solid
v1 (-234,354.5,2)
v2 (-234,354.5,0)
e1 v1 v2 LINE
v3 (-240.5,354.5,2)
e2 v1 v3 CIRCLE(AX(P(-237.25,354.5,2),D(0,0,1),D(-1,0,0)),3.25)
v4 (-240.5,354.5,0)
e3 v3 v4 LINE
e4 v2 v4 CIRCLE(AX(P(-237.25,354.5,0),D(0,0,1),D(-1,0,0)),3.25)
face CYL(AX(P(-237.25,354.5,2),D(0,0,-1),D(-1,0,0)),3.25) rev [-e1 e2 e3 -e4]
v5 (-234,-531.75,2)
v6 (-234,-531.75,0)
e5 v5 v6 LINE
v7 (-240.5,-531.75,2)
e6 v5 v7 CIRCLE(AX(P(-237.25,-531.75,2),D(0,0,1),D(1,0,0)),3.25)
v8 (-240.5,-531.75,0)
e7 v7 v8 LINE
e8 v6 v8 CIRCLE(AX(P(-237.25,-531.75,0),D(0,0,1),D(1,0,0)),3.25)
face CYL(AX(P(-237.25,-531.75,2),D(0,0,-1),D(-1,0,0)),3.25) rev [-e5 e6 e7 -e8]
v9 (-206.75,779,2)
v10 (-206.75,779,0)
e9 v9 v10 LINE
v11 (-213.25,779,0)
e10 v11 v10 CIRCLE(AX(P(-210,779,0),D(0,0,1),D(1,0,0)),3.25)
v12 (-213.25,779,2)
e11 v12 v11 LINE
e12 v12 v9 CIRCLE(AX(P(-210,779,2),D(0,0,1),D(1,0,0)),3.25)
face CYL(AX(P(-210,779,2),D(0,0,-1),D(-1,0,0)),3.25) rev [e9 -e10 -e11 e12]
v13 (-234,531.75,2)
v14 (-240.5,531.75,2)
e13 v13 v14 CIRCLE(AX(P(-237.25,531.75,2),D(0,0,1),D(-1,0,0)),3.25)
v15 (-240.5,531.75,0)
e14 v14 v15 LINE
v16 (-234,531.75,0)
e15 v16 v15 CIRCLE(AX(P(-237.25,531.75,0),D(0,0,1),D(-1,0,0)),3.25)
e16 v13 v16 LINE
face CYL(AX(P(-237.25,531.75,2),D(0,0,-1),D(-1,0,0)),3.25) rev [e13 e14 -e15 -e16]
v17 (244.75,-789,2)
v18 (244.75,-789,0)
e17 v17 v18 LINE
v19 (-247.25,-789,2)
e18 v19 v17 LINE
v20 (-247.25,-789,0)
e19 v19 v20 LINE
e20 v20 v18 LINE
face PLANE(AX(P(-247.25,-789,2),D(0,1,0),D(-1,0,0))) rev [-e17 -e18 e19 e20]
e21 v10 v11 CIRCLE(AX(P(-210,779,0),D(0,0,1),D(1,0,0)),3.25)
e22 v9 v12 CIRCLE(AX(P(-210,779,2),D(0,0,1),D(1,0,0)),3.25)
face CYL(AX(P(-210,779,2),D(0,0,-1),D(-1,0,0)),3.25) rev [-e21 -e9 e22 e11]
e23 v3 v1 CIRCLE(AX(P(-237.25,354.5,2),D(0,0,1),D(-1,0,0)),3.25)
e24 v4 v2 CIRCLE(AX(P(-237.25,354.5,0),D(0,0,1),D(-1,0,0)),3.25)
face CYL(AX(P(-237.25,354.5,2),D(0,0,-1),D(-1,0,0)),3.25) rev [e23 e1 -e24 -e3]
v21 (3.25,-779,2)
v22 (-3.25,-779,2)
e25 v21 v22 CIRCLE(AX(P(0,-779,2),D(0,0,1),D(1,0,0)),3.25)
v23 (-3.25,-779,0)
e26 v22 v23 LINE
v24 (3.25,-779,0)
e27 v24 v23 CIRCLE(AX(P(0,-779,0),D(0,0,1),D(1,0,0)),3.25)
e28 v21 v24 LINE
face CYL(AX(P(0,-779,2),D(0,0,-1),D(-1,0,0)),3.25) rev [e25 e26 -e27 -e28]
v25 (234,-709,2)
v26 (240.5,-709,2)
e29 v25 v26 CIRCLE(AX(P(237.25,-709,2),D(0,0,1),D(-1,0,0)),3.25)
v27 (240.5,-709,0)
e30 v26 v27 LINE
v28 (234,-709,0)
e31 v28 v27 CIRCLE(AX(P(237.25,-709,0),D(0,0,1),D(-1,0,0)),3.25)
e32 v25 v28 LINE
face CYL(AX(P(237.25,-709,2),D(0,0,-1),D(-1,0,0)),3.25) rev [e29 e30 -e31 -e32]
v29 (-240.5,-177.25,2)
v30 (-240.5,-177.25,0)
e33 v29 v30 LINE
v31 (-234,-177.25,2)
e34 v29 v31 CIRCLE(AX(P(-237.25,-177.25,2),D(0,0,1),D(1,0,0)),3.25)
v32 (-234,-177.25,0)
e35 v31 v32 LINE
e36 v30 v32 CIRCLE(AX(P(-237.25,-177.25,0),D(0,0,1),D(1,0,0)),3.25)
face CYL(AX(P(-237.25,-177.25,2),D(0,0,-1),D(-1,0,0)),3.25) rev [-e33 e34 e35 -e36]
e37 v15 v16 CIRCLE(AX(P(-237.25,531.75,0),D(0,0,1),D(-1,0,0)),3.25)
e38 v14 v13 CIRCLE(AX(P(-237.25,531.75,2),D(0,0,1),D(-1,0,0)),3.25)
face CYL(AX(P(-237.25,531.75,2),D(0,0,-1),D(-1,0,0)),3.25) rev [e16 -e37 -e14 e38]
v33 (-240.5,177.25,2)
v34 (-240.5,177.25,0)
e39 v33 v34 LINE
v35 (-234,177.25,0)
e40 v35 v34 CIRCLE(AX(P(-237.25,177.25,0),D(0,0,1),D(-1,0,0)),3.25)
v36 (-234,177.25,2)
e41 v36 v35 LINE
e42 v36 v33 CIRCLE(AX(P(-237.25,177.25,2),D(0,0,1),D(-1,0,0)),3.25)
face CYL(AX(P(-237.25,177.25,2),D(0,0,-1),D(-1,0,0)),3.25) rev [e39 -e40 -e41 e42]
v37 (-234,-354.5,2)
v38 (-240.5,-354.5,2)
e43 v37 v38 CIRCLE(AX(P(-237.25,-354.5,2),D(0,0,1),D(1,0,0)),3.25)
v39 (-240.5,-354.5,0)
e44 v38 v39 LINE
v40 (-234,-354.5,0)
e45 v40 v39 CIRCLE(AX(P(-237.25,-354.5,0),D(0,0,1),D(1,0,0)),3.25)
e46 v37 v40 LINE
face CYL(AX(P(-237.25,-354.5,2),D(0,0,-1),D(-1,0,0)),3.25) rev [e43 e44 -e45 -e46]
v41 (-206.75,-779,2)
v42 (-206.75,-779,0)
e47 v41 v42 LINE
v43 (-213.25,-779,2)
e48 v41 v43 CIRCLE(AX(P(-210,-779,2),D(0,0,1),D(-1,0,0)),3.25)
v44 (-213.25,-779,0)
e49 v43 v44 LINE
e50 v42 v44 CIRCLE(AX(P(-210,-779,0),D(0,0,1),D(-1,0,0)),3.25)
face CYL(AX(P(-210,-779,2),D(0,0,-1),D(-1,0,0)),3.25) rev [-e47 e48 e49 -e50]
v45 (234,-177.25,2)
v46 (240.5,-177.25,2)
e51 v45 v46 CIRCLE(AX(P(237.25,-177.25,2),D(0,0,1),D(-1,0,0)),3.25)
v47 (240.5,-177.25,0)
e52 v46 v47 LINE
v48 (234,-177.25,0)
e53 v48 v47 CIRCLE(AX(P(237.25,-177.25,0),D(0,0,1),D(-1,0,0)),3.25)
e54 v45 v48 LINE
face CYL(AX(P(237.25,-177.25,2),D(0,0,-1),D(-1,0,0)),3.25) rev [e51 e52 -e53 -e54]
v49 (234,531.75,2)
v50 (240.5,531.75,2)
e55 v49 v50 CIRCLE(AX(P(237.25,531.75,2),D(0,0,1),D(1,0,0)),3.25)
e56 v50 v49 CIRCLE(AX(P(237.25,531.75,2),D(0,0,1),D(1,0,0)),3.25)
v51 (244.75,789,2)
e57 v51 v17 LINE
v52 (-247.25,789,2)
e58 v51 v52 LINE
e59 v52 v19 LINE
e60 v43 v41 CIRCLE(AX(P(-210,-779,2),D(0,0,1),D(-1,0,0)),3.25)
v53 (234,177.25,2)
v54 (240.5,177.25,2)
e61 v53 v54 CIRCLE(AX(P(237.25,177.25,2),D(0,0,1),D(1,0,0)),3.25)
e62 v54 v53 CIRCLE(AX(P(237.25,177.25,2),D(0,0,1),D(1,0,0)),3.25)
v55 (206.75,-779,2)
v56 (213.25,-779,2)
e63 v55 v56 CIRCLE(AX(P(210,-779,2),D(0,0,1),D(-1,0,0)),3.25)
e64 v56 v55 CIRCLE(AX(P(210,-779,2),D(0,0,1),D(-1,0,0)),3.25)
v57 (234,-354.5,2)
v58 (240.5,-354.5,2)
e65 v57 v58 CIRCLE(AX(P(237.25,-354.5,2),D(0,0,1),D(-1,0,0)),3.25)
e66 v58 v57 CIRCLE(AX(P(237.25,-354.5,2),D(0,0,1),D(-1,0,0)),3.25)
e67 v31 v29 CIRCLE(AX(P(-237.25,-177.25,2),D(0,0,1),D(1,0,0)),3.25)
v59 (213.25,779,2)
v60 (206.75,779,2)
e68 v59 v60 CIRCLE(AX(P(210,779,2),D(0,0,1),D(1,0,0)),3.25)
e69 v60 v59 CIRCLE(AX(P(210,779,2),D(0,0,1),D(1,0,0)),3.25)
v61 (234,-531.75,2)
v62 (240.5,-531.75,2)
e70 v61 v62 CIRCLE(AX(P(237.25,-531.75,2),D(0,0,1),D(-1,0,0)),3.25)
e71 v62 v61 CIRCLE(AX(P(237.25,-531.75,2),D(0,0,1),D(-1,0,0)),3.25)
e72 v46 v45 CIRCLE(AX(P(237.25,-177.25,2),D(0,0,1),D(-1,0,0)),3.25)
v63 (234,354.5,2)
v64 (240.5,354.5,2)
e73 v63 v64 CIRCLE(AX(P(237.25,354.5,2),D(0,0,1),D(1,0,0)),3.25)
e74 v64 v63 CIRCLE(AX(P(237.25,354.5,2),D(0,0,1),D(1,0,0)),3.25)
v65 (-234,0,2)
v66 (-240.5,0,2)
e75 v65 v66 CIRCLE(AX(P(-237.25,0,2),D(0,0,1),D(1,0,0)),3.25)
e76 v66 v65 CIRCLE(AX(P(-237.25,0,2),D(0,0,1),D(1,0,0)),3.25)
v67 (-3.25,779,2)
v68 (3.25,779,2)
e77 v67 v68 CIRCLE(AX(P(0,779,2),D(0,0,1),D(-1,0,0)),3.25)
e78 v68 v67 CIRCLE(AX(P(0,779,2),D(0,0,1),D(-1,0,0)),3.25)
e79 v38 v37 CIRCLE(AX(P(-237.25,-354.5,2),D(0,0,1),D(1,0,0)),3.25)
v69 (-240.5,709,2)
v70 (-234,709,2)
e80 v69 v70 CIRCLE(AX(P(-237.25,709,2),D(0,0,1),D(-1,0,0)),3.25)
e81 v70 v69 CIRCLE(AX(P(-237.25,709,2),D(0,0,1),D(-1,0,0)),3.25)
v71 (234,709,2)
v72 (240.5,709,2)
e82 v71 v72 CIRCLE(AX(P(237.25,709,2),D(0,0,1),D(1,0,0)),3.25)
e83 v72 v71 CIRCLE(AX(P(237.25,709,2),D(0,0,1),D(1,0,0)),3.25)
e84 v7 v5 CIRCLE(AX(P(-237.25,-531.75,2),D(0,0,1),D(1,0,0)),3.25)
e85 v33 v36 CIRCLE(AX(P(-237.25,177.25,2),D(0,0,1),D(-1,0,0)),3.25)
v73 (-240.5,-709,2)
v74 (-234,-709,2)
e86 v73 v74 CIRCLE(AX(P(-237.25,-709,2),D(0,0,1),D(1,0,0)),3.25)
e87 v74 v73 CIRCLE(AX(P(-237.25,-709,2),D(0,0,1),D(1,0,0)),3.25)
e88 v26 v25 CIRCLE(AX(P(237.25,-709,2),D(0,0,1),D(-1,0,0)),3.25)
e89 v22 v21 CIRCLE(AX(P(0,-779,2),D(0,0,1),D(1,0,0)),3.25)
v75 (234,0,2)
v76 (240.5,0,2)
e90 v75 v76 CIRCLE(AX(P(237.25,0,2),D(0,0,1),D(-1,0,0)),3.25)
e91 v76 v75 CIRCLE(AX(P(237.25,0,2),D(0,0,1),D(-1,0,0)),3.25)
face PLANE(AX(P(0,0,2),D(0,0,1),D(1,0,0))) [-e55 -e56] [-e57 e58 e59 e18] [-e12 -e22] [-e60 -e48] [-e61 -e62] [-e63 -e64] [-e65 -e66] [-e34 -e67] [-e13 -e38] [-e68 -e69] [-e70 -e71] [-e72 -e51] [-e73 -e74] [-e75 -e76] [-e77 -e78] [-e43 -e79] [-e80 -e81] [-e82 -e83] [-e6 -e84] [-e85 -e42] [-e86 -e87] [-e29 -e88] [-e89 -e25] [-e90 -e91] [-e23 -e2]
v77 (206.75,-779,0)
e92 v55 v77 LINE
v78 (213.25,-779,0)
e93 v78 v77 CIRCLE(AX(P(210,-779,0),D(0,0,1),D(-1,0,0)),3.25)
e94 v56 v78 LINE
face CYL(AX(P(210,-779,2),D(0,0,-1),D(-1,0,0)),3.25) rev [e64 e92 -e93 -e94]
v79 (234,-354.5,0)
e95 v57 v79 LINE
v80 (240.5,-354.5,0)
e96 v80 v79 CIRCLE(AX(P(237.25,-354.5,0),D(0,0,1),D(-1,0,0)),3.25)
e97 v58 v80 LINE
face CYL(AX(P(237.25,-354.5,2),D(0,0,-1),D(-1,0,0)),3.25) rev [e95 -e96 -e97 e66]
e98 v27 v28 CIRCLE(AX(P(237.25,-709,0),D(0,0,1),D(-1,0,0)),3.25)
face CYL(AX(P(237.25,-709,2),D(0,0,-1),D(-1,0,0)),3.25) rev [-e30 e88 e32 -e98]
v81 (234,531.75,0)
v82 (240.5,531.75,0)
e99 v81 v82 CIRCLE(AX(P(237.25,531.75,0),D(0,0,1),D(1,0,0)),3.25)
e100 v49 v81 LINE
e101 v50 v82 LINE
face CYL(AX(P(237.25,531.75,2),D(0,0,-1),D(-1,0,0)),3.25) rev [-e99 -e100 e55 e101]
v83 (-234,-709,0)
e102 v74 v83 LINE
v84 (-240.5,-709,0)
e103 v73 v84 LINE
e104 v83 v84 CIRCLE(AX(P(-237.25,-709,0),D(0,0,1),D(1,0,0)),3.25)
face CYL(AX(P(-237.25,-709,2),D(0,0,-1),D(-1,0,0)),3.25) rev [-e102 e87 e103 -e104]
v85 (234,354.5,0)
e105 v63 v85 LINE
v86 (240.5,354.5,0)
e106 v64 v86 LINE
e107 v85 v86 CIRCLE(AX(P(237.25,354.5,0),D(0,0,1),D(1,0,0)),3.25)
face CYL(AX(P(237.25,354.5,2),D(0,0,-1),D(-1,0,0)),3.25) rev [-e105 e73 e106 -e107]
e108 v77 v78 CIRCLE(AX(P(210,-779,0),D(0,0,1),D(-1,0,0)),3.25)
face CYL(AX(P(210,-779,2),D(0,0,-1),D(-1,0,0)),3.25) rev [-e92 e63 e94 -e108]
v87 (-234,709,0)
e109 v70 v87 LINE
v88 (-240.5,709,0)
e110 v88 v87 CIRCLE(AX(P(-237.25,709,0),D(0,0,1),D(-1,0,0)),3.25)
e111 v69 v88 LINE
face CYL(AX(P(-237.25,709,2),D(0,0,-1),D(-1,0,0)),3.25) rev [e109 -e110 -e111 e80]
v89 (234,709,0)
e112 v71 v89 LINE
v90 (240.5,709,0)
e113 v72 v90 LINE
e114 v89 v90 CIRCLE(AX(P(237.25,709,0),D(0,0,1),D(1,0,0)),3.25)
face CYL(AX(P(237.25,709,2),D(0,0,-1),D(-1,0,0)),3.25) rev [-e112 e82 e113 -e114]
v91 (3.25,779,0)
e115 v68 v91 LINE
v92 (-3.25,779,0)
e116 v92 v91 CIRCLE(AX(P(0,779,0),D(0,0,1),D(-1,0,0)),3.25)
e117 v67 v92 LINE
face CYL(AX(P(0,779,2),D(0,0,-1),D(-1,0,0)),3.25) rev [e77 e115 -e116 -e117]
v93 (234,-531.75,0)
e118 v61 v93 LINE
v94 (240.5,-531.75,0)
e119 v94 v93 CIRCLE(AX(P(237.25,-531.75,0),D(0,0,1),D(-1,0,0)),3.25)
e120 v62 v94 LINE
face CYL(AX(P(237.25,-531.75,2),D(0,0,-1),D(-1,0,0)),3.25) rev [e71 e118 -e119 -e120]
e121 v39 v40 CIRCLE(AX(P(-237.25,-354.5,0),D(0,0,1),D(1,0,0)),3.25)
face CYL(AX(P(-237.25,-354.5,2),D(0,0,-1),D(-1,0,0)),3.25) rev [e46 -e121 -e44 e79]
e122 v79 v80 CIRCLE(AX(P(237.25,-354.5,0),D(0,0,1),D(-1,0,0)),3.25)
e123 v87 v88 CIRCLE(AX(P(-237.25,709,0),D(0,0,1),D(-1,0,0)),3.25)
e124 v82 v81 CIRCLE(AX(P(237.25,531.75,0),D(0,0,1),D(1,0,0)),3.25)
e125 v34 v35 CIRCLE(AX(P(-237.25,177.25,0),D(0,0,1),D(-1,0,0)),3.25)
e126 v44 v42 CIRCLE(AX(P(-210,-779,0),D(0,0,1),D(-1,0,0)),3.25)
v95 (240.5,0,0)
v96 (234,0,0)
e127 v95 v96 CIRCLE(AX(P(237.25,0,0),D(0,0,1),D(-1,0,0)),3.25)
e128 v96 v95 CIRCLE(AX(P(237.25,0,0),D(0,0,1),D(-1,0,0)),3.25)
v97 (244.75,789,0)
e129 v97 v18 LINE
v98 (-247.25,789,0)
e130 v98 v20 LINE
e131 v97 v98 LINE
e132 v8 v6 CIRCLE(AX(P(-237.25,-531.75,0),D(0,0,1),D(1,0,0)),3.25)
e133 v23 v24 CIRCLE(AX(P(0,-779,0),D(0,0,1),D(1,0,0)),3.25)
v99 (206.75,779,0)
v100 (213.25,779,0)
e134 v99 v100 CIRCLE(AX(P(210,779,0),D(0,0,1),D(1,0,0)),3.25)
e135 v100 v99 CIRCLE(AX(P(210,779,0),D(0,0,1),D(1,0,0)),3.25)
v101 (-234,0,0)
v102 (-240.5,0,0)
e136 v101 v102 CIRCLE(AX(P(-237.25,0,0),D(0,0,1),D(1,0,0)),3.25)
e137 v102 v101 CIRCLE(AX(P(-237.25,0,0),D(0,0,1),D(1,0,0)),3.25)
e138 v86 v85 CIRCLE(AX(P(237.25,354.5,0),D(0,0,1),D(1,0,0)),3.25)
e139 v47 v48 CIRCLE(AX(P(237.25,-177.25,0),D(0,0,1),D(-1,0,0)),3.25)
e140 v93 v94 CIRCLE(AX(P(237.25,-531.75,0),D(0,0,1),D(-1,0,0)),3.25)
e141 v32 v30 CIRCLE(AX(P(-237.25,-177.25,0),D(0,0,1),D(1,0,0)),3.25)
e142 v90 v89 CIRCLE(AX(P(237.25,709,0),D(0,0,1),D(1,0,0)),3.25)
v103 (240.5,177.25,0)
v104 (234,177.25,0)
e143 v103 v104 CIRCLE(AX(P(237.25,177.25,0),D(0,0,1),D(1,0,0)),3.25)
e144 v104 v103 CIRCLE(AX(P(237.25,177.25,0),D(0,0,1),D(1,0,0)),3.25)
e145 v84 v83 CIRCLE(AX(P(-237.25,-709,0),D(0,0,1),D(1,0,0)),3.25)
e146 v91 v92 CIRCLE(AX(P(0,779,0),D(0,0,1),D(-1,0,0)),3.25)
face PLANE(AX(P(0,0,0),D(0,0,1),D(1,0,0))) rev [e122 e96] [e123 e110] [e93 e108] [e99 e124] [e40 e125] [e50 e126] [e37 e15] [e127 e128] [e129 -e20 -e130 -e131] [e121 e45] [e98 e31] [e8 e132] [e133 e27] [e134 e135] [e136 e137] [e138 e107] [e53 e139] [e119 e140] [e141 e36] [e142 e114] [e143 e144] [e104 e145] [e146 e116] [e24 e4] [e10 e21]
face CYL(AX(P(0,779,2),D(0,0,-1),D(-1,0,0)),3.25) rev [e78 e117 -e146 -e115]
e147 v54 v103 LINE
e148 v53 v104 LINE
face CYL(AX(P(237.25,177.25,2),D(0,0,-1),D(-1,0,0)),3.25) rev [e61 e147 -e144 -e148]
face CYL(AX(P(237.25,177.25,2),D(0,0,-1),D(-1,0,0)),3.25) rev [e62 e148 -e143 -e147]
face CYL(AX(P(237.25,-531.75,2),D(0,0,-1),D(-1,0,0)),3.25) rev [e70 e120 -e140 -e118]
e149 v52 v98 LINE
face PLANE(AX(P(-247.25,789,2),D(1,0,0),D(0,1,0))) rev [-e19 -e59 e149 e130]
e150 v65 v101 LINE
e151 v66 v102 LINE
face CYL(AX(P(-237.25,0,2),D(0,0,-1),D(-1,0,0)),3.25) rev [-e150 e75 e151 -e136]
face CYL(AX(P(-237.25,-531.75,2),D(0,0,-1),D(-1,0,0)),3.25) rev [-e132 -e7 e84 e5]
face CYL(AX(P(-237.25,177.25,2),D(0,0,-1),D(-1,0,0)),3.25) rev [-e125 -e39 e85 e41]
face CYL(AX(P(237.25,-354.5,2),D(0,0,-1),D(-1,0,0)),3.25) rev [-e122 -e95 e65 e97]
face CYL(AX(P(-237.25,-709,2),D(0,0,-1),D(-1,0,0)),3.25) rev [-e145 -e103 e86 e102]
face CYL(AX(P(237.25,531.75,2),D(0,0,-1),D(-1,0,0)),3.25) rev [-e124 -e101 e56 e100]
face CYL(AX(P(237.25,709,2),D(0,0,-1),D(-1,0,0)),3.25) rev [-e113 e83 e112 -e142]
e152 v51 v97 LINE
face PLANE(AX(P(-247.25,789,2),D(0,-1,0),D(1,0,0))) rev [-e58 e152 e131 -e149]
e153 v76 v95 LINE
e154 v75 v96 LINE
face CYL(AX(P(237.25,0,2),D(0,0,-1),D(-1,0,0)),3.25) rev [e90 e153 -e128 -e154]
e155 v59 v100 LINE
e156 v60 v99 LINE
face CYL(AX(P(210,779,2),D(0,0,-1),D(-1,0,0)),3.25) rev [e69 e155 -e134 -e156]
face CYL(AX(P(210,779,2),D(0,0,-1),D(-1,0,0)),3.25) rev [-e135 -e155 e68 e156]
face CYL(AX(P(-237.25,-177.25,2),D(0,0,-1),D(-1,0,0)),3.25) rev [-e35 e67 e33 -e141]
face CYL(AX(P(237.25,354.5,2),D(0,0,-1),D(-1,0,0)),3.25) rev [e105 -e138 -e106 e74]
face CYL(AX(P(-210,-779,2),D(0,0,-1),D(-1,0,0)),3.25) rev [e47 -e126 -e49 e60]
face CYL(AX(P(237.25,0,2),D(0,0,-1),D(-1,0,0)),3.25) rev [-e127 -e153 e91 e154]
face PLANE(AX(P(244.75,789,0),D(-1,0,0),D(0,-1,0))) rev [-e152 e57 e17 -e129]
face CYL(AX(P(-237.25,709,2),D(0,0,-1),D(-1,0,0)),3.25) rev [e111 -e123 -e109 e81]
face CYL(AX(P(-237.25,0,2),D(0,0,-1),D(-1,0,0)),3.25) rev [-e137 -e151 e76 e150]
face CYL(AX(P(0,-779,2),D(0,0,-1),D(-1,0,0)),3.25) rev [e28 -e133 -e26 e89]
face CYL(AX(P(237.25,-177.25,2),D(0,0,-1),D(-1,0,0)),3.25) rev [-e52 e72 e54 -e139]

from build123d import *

# Parameters (mm, degrees)
SKETCH_1_W          = 494.5
SKETCH_1_H          = 1578
SKETCH_1_R          = 3.25
EXTRUDE_1_DEPTH     = 2
SKETCH_2_W          = 2.5
SKETCH_2_H          = 2
CUT_EXTRUDE_1_DEPTH = 1598.254069489


with BuildPart() as part:
    # 草图1 → 凸台-拉伸1 (new body)
    with BuildSketch(Plane.XY):
        Rectangle(SKETCH_1_W, SKETCH_1_H)
        with Locations((-237.25, 0)):
            Circle(SKETCH_1_R, mode=Mode.SUBTRACT)
        with Locations((-237.25, -177.25)):
            Circle(SKETCH_1_R, mode=Mode.SUBTRACT)
        with Locations((-237.25, -354.5)):
            Circle(SKETCH_1_R, mode=Mode.SUBTRACT)
        with Locations((-237.25, -531.75)):
            Circle(SKETCH_1_R, mode=Mode.SUBTRACT)
        with Locations((-237.25, -709)):
            Circle(SKETCH_1_R, mode=Mode.SUBTRACT)
        with Locations((0, -779)):
            Circle(SKETCH_1_R, mode=Mode.SUBTRACT)
        with Locations(Location((0, 779, 0), (0, 0, 180))):
            Circle(SKETCH_1_R, mode=Mode.SUBTRACT)
        with Locations(Location((-237.25, 709, 0), (0, 0, 180))):
            Circle(SKETCH_1_R, mode=Mode.SUBTRACT)
        with Locations(Location((-237.25, 531.75, 0), (0, 0, 180))):
            Circle(SKETCH_1_R, mode=Mode.SUBTRACT)
        with Locations(Location((-237.25, 354.5, 0), (0, 0, 180))):
            Circle(SKETCH_1_R, mode=Mode.SUBTRACT)
        with Locations(Location((-237.25, 177.25, 0), (0, 0, 180))):
            Circle(SKETCH_1_R, mode=Mode.SUBTRACT)
        with Locations((237.25, 177.25)):
            Circle(SKETCH_1_R, mode=Mode.SUBTRACT)
        with Locations((237.25, 354.5)):
            Circle(SKETCH_1_R, mode=Mode.SUBTRACT)
        with Locations((237.25, 531.75)):
            Circle(SKETCH_1_R, mode=Mode.SUBTRACT)
        with Locations((237.25, 709)):
            Circle(SKETCH_1_R, mode=Mode.SUBTRACT)
        with Locations(Location((237.25, -709, 0), (0, 0, 180))):
            Circle(SKETCH_1_R, mode=Mode.SUBTRACT)
        with Locations(Location((237.25, -531.75, 0), (0, 0, 180))):
            Circle(SKETCH_1_R, mode=Mode.SUBTRACT)
        with Locations(Location((237.25, -354.5, 0), (0, 0, 180))):
            Circle(SKETCH_1_R, mode=Mode.SUBTRACT)
        with Locations(Location((237.25, -177.25, 0), (0, 0, 180))):
            Circle(SKETCH_1_R, mode=Mode.SUBTRACT)
        with Locations(Location((237.25, 0, 0), (0, 0, 180))):
            Circle(SKETCH_1_R, mode=Mode.SUBTRACT)
        with Locations((-210, 779)):
            Circle(SKETCH_1_R, mode=Mode.SUBTRACT)
        with Locations((210, 779)):
            Circle(SKETCH_1_R, mode=Mode.SUBTRACT)
        with Locations(Location((210, -779, 0), (0, 0, 180))):
            Circle(SKETCH_1_R, mode=Mode.SUBTRACT)
        with Locations(Location((-210, -779, 0), (0, 0, 180))):
            Circle(SKETCH_1_R, mode=Mode.SUBTRACT)
    extrude(amount=EXTRUDE_1_DEPTH)

    # 草图2 → 切除-拉伸1 (cut, through all)
    with BuildSketch(Plane.XZ.offset(789)):
        with Locations((246, 1)):
            Rectangle(SKETCH_2_W, SKETCH_2_H)
    extrude(amount=-CUT_EXTRUDE_1_DEPTH, mode=Mode.SUBTRACT)


solid = part.part
